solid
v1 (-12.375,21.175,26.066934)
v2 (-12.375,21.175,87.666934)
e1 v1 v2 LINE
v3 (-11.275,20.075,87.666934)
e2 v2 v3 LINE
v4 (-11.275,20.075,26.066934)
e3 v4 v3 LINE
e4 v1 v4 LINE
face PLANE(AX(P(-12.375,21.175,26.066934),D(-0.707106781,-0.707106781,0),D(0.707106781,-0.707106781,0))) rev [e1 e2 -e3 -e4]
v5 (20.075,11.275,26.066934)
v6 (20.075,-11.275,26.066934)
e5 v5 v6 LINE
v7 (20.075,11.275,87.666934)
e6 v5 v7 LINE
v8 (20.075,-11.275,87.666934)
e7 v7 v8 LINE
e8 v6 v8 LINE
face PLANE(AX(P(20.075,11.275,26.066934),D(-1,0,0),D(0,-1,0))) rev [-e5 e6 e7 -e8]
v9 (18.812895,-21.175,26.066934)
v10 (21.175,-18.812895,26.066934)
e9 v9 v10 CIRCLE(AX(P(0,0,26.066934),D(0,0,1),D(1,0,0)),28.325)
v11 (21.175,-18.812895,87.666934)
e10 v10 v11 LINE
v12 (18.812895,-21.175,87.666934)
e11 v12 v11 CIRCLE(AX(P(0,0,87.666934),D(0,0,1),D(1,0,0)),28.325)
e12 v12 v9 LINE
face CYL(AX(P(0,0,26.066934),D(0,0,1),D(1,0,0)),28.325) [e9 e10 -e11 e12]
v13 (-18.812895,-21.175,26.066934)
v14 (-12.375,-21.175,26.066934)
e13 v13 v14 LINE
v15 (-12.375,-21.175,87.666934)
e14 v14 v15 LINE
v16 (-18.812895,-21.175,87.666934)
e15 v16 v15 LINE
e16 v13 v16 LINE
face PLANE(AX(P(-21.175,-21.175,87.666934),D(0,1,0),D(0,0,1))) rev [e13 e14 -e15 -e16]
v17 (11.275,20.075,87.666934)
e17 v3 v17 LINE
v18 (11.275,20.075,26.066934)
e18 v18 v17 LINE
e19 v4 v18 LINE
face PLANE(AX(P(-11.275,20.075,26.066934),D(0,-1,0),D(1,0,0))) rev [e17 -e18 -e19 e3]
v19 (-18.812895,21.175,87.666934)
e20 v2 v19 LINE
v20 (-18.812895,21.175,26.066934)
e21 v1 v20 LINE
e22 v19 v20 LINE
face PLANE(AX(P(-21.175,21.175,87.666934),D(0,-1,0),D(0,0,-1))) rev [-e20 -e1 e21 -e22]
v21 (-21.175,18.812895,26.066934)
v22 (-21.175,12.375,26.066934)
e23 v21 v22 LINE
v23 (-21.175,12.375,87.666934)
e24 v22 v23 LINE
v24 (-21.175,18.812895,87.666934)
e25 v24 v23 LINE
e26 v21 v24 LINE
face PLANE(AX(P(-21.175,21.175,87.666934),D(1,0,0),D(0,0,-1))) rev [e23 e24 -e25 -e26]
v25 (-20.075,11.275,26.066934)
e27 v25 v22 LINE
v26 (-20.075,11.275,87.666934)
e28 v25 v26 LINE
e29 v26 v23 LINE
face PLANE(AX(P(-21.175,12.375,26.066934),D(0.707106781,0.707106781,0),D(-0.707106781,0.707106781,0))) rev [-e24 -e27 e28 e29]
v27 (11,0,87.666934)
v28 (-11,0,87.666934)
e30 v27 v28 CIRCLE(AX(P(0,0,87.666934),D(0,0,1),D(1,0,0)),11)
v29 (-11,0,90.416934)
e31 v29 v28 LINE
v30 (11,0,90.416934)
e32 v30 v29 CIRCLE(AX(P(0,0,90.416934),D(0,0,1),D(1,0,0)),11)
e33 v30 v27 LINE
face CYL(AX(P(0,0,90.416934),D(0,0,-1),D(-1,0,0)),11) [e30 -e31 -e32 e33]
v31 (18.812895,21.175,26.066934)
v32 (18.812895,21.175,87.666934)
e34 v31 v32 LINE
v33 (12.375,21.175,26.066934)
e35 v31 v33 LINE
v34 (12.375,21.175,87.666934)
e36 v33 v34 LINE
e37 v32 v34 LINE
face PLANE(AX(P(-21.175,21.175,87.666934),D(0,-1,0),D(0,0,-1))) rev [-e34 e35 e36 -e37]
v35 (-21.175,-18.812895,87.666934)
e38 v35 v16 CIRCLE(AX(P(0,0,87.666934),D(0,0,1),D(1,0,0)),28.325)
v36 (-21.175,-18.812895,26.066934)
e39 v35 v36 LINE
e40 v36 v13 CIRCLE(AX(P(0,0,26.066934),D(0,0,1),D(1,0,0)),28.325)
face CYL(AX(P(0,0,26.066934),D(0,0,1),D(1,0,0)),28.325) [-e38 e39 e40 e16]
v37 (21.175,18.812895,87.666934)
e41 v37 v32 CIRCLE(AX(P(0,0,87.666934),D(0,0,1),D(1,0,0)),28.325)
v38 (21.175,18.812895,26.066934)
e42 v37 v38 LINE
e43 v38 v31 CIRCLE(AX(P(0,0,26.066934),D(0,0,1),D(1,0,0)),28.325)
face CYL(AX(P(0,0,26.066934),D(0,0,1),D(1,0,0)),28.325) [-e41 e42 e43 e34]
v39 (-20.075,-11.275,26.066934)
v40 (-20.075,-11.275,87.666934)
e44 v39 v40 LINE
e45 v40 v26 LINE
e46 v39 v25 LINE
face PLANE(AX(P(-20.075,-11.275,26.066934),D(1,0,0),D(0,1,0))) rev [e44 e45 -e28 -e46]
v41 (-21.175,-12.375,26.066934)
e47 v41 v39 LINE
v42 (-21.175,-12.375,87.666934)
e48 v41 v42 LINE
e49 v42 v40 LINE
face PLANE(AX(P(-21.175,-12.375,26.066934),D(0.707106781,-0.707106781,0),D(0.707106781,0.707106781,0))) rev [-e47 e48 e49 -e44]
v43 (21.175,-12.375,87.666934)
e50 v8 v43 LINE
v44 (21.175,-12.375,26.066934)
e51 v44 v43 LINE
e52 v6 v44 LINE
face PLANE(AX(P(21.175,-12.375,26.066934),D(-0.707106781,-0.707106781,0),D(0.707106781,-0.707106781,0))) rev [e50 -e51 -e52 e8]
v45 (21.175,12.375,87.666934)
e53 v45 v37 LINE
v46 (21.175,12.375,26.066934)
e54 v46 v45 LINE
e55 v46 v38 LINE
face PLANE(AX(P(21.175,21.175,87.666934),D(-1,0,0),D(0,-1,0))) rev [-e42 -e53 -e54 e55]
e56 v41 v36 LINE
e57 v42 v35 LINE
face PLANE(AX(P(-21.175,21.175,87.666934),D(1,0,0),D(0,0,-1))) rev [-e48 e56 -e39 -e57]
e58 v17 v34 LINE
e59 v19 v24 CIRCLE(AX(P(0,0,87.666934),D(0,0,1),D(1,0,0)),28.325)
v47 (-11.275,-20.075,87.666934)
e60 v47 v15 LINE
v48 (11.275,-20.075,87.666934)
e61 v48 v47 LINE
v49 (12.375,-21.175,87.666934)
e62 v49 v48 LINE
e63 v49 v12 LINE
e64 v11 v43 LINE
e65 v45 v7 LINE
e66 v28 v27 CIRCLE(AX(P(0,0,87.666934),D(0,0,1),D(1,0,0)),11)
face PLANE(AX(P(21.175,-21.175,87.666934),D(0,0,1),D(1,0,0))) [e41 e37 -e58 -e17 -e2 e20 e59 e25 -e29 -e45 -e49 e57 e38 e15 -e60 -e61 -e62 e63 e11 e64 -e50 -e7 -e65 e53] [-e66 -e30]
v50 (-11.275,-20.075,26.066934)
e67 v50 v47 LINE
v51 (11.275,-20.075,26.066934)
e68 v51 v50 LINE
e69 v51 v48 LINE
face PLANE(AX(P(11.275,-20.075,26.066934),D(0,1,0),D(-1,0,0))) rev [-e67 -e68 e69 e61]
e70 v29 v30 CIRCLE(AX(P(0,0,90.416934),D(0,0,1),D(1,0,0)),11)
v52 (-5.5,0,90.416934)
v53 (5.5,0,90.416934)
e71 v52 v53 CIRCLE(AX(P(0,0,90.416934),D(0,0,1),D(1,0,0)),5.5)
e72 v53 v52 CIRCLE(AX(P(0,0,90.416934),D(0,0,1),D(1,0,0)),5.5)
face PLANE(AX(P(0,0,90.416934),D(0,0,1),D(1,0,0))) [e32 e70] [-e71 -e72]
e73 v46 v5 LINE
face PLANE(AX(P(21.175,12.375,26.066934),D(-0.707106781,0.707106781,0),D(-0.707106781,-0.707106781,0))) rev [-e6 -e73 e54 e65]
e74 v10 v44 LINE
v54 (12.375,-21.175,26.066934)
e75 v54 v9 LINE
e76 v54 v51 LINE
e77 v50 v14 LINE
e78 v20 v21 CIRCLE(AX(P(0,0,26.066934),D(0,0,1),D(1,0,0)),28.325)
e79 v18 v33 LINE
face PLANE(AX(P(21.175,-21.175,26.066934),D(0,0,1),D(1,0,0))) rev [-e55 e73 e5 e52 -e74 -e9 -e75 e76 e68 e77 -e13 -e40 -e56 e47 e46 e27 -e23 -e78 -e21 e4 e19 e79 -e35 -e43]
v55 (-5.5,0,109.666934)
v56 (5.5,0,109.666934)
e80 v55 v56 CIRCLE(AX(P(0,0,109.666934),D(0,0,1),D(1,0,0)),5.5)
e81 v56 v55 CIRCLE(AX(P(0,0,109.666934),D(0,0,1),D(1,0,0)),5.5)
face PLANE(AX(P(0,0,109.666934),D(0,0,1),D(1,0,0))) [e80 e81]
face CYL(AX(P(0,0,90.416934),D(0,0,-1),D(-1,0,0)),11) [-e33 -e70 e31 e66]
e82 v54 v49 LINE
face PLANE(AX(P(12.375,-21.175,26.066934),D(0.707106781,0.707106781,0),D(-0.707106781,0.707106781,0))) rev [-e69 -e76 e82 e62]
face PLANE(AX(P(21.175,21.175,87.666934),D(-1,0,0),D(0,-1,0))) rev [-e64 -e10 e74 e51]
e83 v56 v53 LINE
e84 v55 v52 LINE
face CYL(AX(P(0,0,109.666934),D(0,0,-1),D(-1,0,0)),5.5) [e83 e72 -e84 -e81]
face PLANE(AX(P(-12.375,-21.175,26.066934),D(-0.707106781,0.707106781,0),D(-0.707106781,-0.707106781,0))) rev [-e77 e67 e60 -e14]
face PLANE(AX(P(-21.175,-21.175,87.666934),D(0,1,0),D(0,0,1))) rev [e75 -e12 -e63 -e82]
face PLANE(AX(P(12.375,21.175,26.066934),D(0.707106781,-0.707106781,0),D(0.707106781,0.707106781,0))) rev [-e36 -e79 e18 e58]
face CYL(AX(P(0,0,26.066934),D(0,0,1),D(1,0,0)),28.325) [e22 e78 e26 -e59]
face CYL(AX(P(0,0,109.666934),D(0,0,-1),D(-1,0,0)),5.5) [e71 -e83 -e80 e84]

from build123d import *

# Parameters (mm, degrees)
SKETCH1_W           = 77
SKETCH1_H           = 77
EXTRUDE1_DEPTH      = 112
SKETCH3_R           = 58.910335971
SKETCH3_R_2         = 51.5
EXTRUDE3_DEPTH      = 125.533128123
EXTRUDE7_DEPTH      = 125.533128123
SKETCH2_R           = 10
EXTRUDE10_DEPTH     = 80
CIRPATTERN3_COUNT   = 4
EXTRUDE13_START     = 5
SKETCH11_R          = 20
SKETCH11_R_2        = 10
EXTRUDE13_DEPTH     = 5
BOSS_EXTRUDE1_START = 120
SKETCH12_R          = 10
BOSS_EXTRUDE1_DEPTH = 120
SCALE1_SCALE        = 0.55


with BuildPart() as part:
    # Sketch1 → Extrude1 (new body)
    with BuildSketch(Plane.XY):
        Rectangle(SKETCH1_W, SKETCH1_H)
    extrude(amount=EXTRUDE1_DEPTH)

    # Sketch3 → Extrude3 (cut, through all)
    with BuildSketch(Plane.XY.offset(112)):
        Circle(SKETCH3_R)
        Circle(SKETCH3_R_2, mode=Mode.SUBTRACT)
    extrude(amount=-EXTRUDE3_DEPTH, mode=Mode.SUBTRACT)

    # Sketch7 → Extrude7 (cut, through all)
    with BuildSketch(Plane.XY.offset(112)):
        Polygon((-22.5, 38.5), (22.5, 38.5), (20.5, 36.5), (-20.5, 36.5), align=None)
    extrude7 = extrude(amount=-EXTRUDE7_DEPTH, mode=Mode.SUBTRACT)

    # Sketch2 → Extrude10 (cut)
    with BuildSketch(Plane.XY.offset(112)):
        Circle(SKETCH2_R)
    extrude(amount=-EXTRUDE10_DEPTH, mode=Mode.SUBTRACT)

    # CirPattern3: Extrude7 ×4 about axis
    cirpattern3_axis = Axis((0, 0, 0), (0, 0, 1))
    for i in range(1, CIRPATTERN3_COUNT):
        add(extrude7.rotate(cirpattern3_axis, i * 360 / CIRPATTERN3_COUNT), mode=Mode.SUBTRACT)

    # Sketch11 → Extrude13 (add)
    with BuildSketch(Plane.XY.offset(112).offset(EXTRUDE13_START)):
        Circle(SKETCH11_R)
        Circle(SKETCH11_R_2, mode=Mode.SUBTRACT)
    extrude(amount=-EXTRUDE13_DEPTH)

    # Sketch12 → Boss-Extrude1 (add)
    with BuildSketch(Plane.XY.offset(32).offset(BOSS_EXTRUDE1_START)):
        Circle(SKETCH12_R)
    extrude(amount=-BOSS_EXTRUDE1_DEPTH)


with BuildPart() as part_1:
    # Scale1: scaled about (0, 0, 57.926521071)
    add(part.part.scale(SCALE1_SCALE).moved(Location((0, 0, 26.066934482))))


solid = part_1.part
